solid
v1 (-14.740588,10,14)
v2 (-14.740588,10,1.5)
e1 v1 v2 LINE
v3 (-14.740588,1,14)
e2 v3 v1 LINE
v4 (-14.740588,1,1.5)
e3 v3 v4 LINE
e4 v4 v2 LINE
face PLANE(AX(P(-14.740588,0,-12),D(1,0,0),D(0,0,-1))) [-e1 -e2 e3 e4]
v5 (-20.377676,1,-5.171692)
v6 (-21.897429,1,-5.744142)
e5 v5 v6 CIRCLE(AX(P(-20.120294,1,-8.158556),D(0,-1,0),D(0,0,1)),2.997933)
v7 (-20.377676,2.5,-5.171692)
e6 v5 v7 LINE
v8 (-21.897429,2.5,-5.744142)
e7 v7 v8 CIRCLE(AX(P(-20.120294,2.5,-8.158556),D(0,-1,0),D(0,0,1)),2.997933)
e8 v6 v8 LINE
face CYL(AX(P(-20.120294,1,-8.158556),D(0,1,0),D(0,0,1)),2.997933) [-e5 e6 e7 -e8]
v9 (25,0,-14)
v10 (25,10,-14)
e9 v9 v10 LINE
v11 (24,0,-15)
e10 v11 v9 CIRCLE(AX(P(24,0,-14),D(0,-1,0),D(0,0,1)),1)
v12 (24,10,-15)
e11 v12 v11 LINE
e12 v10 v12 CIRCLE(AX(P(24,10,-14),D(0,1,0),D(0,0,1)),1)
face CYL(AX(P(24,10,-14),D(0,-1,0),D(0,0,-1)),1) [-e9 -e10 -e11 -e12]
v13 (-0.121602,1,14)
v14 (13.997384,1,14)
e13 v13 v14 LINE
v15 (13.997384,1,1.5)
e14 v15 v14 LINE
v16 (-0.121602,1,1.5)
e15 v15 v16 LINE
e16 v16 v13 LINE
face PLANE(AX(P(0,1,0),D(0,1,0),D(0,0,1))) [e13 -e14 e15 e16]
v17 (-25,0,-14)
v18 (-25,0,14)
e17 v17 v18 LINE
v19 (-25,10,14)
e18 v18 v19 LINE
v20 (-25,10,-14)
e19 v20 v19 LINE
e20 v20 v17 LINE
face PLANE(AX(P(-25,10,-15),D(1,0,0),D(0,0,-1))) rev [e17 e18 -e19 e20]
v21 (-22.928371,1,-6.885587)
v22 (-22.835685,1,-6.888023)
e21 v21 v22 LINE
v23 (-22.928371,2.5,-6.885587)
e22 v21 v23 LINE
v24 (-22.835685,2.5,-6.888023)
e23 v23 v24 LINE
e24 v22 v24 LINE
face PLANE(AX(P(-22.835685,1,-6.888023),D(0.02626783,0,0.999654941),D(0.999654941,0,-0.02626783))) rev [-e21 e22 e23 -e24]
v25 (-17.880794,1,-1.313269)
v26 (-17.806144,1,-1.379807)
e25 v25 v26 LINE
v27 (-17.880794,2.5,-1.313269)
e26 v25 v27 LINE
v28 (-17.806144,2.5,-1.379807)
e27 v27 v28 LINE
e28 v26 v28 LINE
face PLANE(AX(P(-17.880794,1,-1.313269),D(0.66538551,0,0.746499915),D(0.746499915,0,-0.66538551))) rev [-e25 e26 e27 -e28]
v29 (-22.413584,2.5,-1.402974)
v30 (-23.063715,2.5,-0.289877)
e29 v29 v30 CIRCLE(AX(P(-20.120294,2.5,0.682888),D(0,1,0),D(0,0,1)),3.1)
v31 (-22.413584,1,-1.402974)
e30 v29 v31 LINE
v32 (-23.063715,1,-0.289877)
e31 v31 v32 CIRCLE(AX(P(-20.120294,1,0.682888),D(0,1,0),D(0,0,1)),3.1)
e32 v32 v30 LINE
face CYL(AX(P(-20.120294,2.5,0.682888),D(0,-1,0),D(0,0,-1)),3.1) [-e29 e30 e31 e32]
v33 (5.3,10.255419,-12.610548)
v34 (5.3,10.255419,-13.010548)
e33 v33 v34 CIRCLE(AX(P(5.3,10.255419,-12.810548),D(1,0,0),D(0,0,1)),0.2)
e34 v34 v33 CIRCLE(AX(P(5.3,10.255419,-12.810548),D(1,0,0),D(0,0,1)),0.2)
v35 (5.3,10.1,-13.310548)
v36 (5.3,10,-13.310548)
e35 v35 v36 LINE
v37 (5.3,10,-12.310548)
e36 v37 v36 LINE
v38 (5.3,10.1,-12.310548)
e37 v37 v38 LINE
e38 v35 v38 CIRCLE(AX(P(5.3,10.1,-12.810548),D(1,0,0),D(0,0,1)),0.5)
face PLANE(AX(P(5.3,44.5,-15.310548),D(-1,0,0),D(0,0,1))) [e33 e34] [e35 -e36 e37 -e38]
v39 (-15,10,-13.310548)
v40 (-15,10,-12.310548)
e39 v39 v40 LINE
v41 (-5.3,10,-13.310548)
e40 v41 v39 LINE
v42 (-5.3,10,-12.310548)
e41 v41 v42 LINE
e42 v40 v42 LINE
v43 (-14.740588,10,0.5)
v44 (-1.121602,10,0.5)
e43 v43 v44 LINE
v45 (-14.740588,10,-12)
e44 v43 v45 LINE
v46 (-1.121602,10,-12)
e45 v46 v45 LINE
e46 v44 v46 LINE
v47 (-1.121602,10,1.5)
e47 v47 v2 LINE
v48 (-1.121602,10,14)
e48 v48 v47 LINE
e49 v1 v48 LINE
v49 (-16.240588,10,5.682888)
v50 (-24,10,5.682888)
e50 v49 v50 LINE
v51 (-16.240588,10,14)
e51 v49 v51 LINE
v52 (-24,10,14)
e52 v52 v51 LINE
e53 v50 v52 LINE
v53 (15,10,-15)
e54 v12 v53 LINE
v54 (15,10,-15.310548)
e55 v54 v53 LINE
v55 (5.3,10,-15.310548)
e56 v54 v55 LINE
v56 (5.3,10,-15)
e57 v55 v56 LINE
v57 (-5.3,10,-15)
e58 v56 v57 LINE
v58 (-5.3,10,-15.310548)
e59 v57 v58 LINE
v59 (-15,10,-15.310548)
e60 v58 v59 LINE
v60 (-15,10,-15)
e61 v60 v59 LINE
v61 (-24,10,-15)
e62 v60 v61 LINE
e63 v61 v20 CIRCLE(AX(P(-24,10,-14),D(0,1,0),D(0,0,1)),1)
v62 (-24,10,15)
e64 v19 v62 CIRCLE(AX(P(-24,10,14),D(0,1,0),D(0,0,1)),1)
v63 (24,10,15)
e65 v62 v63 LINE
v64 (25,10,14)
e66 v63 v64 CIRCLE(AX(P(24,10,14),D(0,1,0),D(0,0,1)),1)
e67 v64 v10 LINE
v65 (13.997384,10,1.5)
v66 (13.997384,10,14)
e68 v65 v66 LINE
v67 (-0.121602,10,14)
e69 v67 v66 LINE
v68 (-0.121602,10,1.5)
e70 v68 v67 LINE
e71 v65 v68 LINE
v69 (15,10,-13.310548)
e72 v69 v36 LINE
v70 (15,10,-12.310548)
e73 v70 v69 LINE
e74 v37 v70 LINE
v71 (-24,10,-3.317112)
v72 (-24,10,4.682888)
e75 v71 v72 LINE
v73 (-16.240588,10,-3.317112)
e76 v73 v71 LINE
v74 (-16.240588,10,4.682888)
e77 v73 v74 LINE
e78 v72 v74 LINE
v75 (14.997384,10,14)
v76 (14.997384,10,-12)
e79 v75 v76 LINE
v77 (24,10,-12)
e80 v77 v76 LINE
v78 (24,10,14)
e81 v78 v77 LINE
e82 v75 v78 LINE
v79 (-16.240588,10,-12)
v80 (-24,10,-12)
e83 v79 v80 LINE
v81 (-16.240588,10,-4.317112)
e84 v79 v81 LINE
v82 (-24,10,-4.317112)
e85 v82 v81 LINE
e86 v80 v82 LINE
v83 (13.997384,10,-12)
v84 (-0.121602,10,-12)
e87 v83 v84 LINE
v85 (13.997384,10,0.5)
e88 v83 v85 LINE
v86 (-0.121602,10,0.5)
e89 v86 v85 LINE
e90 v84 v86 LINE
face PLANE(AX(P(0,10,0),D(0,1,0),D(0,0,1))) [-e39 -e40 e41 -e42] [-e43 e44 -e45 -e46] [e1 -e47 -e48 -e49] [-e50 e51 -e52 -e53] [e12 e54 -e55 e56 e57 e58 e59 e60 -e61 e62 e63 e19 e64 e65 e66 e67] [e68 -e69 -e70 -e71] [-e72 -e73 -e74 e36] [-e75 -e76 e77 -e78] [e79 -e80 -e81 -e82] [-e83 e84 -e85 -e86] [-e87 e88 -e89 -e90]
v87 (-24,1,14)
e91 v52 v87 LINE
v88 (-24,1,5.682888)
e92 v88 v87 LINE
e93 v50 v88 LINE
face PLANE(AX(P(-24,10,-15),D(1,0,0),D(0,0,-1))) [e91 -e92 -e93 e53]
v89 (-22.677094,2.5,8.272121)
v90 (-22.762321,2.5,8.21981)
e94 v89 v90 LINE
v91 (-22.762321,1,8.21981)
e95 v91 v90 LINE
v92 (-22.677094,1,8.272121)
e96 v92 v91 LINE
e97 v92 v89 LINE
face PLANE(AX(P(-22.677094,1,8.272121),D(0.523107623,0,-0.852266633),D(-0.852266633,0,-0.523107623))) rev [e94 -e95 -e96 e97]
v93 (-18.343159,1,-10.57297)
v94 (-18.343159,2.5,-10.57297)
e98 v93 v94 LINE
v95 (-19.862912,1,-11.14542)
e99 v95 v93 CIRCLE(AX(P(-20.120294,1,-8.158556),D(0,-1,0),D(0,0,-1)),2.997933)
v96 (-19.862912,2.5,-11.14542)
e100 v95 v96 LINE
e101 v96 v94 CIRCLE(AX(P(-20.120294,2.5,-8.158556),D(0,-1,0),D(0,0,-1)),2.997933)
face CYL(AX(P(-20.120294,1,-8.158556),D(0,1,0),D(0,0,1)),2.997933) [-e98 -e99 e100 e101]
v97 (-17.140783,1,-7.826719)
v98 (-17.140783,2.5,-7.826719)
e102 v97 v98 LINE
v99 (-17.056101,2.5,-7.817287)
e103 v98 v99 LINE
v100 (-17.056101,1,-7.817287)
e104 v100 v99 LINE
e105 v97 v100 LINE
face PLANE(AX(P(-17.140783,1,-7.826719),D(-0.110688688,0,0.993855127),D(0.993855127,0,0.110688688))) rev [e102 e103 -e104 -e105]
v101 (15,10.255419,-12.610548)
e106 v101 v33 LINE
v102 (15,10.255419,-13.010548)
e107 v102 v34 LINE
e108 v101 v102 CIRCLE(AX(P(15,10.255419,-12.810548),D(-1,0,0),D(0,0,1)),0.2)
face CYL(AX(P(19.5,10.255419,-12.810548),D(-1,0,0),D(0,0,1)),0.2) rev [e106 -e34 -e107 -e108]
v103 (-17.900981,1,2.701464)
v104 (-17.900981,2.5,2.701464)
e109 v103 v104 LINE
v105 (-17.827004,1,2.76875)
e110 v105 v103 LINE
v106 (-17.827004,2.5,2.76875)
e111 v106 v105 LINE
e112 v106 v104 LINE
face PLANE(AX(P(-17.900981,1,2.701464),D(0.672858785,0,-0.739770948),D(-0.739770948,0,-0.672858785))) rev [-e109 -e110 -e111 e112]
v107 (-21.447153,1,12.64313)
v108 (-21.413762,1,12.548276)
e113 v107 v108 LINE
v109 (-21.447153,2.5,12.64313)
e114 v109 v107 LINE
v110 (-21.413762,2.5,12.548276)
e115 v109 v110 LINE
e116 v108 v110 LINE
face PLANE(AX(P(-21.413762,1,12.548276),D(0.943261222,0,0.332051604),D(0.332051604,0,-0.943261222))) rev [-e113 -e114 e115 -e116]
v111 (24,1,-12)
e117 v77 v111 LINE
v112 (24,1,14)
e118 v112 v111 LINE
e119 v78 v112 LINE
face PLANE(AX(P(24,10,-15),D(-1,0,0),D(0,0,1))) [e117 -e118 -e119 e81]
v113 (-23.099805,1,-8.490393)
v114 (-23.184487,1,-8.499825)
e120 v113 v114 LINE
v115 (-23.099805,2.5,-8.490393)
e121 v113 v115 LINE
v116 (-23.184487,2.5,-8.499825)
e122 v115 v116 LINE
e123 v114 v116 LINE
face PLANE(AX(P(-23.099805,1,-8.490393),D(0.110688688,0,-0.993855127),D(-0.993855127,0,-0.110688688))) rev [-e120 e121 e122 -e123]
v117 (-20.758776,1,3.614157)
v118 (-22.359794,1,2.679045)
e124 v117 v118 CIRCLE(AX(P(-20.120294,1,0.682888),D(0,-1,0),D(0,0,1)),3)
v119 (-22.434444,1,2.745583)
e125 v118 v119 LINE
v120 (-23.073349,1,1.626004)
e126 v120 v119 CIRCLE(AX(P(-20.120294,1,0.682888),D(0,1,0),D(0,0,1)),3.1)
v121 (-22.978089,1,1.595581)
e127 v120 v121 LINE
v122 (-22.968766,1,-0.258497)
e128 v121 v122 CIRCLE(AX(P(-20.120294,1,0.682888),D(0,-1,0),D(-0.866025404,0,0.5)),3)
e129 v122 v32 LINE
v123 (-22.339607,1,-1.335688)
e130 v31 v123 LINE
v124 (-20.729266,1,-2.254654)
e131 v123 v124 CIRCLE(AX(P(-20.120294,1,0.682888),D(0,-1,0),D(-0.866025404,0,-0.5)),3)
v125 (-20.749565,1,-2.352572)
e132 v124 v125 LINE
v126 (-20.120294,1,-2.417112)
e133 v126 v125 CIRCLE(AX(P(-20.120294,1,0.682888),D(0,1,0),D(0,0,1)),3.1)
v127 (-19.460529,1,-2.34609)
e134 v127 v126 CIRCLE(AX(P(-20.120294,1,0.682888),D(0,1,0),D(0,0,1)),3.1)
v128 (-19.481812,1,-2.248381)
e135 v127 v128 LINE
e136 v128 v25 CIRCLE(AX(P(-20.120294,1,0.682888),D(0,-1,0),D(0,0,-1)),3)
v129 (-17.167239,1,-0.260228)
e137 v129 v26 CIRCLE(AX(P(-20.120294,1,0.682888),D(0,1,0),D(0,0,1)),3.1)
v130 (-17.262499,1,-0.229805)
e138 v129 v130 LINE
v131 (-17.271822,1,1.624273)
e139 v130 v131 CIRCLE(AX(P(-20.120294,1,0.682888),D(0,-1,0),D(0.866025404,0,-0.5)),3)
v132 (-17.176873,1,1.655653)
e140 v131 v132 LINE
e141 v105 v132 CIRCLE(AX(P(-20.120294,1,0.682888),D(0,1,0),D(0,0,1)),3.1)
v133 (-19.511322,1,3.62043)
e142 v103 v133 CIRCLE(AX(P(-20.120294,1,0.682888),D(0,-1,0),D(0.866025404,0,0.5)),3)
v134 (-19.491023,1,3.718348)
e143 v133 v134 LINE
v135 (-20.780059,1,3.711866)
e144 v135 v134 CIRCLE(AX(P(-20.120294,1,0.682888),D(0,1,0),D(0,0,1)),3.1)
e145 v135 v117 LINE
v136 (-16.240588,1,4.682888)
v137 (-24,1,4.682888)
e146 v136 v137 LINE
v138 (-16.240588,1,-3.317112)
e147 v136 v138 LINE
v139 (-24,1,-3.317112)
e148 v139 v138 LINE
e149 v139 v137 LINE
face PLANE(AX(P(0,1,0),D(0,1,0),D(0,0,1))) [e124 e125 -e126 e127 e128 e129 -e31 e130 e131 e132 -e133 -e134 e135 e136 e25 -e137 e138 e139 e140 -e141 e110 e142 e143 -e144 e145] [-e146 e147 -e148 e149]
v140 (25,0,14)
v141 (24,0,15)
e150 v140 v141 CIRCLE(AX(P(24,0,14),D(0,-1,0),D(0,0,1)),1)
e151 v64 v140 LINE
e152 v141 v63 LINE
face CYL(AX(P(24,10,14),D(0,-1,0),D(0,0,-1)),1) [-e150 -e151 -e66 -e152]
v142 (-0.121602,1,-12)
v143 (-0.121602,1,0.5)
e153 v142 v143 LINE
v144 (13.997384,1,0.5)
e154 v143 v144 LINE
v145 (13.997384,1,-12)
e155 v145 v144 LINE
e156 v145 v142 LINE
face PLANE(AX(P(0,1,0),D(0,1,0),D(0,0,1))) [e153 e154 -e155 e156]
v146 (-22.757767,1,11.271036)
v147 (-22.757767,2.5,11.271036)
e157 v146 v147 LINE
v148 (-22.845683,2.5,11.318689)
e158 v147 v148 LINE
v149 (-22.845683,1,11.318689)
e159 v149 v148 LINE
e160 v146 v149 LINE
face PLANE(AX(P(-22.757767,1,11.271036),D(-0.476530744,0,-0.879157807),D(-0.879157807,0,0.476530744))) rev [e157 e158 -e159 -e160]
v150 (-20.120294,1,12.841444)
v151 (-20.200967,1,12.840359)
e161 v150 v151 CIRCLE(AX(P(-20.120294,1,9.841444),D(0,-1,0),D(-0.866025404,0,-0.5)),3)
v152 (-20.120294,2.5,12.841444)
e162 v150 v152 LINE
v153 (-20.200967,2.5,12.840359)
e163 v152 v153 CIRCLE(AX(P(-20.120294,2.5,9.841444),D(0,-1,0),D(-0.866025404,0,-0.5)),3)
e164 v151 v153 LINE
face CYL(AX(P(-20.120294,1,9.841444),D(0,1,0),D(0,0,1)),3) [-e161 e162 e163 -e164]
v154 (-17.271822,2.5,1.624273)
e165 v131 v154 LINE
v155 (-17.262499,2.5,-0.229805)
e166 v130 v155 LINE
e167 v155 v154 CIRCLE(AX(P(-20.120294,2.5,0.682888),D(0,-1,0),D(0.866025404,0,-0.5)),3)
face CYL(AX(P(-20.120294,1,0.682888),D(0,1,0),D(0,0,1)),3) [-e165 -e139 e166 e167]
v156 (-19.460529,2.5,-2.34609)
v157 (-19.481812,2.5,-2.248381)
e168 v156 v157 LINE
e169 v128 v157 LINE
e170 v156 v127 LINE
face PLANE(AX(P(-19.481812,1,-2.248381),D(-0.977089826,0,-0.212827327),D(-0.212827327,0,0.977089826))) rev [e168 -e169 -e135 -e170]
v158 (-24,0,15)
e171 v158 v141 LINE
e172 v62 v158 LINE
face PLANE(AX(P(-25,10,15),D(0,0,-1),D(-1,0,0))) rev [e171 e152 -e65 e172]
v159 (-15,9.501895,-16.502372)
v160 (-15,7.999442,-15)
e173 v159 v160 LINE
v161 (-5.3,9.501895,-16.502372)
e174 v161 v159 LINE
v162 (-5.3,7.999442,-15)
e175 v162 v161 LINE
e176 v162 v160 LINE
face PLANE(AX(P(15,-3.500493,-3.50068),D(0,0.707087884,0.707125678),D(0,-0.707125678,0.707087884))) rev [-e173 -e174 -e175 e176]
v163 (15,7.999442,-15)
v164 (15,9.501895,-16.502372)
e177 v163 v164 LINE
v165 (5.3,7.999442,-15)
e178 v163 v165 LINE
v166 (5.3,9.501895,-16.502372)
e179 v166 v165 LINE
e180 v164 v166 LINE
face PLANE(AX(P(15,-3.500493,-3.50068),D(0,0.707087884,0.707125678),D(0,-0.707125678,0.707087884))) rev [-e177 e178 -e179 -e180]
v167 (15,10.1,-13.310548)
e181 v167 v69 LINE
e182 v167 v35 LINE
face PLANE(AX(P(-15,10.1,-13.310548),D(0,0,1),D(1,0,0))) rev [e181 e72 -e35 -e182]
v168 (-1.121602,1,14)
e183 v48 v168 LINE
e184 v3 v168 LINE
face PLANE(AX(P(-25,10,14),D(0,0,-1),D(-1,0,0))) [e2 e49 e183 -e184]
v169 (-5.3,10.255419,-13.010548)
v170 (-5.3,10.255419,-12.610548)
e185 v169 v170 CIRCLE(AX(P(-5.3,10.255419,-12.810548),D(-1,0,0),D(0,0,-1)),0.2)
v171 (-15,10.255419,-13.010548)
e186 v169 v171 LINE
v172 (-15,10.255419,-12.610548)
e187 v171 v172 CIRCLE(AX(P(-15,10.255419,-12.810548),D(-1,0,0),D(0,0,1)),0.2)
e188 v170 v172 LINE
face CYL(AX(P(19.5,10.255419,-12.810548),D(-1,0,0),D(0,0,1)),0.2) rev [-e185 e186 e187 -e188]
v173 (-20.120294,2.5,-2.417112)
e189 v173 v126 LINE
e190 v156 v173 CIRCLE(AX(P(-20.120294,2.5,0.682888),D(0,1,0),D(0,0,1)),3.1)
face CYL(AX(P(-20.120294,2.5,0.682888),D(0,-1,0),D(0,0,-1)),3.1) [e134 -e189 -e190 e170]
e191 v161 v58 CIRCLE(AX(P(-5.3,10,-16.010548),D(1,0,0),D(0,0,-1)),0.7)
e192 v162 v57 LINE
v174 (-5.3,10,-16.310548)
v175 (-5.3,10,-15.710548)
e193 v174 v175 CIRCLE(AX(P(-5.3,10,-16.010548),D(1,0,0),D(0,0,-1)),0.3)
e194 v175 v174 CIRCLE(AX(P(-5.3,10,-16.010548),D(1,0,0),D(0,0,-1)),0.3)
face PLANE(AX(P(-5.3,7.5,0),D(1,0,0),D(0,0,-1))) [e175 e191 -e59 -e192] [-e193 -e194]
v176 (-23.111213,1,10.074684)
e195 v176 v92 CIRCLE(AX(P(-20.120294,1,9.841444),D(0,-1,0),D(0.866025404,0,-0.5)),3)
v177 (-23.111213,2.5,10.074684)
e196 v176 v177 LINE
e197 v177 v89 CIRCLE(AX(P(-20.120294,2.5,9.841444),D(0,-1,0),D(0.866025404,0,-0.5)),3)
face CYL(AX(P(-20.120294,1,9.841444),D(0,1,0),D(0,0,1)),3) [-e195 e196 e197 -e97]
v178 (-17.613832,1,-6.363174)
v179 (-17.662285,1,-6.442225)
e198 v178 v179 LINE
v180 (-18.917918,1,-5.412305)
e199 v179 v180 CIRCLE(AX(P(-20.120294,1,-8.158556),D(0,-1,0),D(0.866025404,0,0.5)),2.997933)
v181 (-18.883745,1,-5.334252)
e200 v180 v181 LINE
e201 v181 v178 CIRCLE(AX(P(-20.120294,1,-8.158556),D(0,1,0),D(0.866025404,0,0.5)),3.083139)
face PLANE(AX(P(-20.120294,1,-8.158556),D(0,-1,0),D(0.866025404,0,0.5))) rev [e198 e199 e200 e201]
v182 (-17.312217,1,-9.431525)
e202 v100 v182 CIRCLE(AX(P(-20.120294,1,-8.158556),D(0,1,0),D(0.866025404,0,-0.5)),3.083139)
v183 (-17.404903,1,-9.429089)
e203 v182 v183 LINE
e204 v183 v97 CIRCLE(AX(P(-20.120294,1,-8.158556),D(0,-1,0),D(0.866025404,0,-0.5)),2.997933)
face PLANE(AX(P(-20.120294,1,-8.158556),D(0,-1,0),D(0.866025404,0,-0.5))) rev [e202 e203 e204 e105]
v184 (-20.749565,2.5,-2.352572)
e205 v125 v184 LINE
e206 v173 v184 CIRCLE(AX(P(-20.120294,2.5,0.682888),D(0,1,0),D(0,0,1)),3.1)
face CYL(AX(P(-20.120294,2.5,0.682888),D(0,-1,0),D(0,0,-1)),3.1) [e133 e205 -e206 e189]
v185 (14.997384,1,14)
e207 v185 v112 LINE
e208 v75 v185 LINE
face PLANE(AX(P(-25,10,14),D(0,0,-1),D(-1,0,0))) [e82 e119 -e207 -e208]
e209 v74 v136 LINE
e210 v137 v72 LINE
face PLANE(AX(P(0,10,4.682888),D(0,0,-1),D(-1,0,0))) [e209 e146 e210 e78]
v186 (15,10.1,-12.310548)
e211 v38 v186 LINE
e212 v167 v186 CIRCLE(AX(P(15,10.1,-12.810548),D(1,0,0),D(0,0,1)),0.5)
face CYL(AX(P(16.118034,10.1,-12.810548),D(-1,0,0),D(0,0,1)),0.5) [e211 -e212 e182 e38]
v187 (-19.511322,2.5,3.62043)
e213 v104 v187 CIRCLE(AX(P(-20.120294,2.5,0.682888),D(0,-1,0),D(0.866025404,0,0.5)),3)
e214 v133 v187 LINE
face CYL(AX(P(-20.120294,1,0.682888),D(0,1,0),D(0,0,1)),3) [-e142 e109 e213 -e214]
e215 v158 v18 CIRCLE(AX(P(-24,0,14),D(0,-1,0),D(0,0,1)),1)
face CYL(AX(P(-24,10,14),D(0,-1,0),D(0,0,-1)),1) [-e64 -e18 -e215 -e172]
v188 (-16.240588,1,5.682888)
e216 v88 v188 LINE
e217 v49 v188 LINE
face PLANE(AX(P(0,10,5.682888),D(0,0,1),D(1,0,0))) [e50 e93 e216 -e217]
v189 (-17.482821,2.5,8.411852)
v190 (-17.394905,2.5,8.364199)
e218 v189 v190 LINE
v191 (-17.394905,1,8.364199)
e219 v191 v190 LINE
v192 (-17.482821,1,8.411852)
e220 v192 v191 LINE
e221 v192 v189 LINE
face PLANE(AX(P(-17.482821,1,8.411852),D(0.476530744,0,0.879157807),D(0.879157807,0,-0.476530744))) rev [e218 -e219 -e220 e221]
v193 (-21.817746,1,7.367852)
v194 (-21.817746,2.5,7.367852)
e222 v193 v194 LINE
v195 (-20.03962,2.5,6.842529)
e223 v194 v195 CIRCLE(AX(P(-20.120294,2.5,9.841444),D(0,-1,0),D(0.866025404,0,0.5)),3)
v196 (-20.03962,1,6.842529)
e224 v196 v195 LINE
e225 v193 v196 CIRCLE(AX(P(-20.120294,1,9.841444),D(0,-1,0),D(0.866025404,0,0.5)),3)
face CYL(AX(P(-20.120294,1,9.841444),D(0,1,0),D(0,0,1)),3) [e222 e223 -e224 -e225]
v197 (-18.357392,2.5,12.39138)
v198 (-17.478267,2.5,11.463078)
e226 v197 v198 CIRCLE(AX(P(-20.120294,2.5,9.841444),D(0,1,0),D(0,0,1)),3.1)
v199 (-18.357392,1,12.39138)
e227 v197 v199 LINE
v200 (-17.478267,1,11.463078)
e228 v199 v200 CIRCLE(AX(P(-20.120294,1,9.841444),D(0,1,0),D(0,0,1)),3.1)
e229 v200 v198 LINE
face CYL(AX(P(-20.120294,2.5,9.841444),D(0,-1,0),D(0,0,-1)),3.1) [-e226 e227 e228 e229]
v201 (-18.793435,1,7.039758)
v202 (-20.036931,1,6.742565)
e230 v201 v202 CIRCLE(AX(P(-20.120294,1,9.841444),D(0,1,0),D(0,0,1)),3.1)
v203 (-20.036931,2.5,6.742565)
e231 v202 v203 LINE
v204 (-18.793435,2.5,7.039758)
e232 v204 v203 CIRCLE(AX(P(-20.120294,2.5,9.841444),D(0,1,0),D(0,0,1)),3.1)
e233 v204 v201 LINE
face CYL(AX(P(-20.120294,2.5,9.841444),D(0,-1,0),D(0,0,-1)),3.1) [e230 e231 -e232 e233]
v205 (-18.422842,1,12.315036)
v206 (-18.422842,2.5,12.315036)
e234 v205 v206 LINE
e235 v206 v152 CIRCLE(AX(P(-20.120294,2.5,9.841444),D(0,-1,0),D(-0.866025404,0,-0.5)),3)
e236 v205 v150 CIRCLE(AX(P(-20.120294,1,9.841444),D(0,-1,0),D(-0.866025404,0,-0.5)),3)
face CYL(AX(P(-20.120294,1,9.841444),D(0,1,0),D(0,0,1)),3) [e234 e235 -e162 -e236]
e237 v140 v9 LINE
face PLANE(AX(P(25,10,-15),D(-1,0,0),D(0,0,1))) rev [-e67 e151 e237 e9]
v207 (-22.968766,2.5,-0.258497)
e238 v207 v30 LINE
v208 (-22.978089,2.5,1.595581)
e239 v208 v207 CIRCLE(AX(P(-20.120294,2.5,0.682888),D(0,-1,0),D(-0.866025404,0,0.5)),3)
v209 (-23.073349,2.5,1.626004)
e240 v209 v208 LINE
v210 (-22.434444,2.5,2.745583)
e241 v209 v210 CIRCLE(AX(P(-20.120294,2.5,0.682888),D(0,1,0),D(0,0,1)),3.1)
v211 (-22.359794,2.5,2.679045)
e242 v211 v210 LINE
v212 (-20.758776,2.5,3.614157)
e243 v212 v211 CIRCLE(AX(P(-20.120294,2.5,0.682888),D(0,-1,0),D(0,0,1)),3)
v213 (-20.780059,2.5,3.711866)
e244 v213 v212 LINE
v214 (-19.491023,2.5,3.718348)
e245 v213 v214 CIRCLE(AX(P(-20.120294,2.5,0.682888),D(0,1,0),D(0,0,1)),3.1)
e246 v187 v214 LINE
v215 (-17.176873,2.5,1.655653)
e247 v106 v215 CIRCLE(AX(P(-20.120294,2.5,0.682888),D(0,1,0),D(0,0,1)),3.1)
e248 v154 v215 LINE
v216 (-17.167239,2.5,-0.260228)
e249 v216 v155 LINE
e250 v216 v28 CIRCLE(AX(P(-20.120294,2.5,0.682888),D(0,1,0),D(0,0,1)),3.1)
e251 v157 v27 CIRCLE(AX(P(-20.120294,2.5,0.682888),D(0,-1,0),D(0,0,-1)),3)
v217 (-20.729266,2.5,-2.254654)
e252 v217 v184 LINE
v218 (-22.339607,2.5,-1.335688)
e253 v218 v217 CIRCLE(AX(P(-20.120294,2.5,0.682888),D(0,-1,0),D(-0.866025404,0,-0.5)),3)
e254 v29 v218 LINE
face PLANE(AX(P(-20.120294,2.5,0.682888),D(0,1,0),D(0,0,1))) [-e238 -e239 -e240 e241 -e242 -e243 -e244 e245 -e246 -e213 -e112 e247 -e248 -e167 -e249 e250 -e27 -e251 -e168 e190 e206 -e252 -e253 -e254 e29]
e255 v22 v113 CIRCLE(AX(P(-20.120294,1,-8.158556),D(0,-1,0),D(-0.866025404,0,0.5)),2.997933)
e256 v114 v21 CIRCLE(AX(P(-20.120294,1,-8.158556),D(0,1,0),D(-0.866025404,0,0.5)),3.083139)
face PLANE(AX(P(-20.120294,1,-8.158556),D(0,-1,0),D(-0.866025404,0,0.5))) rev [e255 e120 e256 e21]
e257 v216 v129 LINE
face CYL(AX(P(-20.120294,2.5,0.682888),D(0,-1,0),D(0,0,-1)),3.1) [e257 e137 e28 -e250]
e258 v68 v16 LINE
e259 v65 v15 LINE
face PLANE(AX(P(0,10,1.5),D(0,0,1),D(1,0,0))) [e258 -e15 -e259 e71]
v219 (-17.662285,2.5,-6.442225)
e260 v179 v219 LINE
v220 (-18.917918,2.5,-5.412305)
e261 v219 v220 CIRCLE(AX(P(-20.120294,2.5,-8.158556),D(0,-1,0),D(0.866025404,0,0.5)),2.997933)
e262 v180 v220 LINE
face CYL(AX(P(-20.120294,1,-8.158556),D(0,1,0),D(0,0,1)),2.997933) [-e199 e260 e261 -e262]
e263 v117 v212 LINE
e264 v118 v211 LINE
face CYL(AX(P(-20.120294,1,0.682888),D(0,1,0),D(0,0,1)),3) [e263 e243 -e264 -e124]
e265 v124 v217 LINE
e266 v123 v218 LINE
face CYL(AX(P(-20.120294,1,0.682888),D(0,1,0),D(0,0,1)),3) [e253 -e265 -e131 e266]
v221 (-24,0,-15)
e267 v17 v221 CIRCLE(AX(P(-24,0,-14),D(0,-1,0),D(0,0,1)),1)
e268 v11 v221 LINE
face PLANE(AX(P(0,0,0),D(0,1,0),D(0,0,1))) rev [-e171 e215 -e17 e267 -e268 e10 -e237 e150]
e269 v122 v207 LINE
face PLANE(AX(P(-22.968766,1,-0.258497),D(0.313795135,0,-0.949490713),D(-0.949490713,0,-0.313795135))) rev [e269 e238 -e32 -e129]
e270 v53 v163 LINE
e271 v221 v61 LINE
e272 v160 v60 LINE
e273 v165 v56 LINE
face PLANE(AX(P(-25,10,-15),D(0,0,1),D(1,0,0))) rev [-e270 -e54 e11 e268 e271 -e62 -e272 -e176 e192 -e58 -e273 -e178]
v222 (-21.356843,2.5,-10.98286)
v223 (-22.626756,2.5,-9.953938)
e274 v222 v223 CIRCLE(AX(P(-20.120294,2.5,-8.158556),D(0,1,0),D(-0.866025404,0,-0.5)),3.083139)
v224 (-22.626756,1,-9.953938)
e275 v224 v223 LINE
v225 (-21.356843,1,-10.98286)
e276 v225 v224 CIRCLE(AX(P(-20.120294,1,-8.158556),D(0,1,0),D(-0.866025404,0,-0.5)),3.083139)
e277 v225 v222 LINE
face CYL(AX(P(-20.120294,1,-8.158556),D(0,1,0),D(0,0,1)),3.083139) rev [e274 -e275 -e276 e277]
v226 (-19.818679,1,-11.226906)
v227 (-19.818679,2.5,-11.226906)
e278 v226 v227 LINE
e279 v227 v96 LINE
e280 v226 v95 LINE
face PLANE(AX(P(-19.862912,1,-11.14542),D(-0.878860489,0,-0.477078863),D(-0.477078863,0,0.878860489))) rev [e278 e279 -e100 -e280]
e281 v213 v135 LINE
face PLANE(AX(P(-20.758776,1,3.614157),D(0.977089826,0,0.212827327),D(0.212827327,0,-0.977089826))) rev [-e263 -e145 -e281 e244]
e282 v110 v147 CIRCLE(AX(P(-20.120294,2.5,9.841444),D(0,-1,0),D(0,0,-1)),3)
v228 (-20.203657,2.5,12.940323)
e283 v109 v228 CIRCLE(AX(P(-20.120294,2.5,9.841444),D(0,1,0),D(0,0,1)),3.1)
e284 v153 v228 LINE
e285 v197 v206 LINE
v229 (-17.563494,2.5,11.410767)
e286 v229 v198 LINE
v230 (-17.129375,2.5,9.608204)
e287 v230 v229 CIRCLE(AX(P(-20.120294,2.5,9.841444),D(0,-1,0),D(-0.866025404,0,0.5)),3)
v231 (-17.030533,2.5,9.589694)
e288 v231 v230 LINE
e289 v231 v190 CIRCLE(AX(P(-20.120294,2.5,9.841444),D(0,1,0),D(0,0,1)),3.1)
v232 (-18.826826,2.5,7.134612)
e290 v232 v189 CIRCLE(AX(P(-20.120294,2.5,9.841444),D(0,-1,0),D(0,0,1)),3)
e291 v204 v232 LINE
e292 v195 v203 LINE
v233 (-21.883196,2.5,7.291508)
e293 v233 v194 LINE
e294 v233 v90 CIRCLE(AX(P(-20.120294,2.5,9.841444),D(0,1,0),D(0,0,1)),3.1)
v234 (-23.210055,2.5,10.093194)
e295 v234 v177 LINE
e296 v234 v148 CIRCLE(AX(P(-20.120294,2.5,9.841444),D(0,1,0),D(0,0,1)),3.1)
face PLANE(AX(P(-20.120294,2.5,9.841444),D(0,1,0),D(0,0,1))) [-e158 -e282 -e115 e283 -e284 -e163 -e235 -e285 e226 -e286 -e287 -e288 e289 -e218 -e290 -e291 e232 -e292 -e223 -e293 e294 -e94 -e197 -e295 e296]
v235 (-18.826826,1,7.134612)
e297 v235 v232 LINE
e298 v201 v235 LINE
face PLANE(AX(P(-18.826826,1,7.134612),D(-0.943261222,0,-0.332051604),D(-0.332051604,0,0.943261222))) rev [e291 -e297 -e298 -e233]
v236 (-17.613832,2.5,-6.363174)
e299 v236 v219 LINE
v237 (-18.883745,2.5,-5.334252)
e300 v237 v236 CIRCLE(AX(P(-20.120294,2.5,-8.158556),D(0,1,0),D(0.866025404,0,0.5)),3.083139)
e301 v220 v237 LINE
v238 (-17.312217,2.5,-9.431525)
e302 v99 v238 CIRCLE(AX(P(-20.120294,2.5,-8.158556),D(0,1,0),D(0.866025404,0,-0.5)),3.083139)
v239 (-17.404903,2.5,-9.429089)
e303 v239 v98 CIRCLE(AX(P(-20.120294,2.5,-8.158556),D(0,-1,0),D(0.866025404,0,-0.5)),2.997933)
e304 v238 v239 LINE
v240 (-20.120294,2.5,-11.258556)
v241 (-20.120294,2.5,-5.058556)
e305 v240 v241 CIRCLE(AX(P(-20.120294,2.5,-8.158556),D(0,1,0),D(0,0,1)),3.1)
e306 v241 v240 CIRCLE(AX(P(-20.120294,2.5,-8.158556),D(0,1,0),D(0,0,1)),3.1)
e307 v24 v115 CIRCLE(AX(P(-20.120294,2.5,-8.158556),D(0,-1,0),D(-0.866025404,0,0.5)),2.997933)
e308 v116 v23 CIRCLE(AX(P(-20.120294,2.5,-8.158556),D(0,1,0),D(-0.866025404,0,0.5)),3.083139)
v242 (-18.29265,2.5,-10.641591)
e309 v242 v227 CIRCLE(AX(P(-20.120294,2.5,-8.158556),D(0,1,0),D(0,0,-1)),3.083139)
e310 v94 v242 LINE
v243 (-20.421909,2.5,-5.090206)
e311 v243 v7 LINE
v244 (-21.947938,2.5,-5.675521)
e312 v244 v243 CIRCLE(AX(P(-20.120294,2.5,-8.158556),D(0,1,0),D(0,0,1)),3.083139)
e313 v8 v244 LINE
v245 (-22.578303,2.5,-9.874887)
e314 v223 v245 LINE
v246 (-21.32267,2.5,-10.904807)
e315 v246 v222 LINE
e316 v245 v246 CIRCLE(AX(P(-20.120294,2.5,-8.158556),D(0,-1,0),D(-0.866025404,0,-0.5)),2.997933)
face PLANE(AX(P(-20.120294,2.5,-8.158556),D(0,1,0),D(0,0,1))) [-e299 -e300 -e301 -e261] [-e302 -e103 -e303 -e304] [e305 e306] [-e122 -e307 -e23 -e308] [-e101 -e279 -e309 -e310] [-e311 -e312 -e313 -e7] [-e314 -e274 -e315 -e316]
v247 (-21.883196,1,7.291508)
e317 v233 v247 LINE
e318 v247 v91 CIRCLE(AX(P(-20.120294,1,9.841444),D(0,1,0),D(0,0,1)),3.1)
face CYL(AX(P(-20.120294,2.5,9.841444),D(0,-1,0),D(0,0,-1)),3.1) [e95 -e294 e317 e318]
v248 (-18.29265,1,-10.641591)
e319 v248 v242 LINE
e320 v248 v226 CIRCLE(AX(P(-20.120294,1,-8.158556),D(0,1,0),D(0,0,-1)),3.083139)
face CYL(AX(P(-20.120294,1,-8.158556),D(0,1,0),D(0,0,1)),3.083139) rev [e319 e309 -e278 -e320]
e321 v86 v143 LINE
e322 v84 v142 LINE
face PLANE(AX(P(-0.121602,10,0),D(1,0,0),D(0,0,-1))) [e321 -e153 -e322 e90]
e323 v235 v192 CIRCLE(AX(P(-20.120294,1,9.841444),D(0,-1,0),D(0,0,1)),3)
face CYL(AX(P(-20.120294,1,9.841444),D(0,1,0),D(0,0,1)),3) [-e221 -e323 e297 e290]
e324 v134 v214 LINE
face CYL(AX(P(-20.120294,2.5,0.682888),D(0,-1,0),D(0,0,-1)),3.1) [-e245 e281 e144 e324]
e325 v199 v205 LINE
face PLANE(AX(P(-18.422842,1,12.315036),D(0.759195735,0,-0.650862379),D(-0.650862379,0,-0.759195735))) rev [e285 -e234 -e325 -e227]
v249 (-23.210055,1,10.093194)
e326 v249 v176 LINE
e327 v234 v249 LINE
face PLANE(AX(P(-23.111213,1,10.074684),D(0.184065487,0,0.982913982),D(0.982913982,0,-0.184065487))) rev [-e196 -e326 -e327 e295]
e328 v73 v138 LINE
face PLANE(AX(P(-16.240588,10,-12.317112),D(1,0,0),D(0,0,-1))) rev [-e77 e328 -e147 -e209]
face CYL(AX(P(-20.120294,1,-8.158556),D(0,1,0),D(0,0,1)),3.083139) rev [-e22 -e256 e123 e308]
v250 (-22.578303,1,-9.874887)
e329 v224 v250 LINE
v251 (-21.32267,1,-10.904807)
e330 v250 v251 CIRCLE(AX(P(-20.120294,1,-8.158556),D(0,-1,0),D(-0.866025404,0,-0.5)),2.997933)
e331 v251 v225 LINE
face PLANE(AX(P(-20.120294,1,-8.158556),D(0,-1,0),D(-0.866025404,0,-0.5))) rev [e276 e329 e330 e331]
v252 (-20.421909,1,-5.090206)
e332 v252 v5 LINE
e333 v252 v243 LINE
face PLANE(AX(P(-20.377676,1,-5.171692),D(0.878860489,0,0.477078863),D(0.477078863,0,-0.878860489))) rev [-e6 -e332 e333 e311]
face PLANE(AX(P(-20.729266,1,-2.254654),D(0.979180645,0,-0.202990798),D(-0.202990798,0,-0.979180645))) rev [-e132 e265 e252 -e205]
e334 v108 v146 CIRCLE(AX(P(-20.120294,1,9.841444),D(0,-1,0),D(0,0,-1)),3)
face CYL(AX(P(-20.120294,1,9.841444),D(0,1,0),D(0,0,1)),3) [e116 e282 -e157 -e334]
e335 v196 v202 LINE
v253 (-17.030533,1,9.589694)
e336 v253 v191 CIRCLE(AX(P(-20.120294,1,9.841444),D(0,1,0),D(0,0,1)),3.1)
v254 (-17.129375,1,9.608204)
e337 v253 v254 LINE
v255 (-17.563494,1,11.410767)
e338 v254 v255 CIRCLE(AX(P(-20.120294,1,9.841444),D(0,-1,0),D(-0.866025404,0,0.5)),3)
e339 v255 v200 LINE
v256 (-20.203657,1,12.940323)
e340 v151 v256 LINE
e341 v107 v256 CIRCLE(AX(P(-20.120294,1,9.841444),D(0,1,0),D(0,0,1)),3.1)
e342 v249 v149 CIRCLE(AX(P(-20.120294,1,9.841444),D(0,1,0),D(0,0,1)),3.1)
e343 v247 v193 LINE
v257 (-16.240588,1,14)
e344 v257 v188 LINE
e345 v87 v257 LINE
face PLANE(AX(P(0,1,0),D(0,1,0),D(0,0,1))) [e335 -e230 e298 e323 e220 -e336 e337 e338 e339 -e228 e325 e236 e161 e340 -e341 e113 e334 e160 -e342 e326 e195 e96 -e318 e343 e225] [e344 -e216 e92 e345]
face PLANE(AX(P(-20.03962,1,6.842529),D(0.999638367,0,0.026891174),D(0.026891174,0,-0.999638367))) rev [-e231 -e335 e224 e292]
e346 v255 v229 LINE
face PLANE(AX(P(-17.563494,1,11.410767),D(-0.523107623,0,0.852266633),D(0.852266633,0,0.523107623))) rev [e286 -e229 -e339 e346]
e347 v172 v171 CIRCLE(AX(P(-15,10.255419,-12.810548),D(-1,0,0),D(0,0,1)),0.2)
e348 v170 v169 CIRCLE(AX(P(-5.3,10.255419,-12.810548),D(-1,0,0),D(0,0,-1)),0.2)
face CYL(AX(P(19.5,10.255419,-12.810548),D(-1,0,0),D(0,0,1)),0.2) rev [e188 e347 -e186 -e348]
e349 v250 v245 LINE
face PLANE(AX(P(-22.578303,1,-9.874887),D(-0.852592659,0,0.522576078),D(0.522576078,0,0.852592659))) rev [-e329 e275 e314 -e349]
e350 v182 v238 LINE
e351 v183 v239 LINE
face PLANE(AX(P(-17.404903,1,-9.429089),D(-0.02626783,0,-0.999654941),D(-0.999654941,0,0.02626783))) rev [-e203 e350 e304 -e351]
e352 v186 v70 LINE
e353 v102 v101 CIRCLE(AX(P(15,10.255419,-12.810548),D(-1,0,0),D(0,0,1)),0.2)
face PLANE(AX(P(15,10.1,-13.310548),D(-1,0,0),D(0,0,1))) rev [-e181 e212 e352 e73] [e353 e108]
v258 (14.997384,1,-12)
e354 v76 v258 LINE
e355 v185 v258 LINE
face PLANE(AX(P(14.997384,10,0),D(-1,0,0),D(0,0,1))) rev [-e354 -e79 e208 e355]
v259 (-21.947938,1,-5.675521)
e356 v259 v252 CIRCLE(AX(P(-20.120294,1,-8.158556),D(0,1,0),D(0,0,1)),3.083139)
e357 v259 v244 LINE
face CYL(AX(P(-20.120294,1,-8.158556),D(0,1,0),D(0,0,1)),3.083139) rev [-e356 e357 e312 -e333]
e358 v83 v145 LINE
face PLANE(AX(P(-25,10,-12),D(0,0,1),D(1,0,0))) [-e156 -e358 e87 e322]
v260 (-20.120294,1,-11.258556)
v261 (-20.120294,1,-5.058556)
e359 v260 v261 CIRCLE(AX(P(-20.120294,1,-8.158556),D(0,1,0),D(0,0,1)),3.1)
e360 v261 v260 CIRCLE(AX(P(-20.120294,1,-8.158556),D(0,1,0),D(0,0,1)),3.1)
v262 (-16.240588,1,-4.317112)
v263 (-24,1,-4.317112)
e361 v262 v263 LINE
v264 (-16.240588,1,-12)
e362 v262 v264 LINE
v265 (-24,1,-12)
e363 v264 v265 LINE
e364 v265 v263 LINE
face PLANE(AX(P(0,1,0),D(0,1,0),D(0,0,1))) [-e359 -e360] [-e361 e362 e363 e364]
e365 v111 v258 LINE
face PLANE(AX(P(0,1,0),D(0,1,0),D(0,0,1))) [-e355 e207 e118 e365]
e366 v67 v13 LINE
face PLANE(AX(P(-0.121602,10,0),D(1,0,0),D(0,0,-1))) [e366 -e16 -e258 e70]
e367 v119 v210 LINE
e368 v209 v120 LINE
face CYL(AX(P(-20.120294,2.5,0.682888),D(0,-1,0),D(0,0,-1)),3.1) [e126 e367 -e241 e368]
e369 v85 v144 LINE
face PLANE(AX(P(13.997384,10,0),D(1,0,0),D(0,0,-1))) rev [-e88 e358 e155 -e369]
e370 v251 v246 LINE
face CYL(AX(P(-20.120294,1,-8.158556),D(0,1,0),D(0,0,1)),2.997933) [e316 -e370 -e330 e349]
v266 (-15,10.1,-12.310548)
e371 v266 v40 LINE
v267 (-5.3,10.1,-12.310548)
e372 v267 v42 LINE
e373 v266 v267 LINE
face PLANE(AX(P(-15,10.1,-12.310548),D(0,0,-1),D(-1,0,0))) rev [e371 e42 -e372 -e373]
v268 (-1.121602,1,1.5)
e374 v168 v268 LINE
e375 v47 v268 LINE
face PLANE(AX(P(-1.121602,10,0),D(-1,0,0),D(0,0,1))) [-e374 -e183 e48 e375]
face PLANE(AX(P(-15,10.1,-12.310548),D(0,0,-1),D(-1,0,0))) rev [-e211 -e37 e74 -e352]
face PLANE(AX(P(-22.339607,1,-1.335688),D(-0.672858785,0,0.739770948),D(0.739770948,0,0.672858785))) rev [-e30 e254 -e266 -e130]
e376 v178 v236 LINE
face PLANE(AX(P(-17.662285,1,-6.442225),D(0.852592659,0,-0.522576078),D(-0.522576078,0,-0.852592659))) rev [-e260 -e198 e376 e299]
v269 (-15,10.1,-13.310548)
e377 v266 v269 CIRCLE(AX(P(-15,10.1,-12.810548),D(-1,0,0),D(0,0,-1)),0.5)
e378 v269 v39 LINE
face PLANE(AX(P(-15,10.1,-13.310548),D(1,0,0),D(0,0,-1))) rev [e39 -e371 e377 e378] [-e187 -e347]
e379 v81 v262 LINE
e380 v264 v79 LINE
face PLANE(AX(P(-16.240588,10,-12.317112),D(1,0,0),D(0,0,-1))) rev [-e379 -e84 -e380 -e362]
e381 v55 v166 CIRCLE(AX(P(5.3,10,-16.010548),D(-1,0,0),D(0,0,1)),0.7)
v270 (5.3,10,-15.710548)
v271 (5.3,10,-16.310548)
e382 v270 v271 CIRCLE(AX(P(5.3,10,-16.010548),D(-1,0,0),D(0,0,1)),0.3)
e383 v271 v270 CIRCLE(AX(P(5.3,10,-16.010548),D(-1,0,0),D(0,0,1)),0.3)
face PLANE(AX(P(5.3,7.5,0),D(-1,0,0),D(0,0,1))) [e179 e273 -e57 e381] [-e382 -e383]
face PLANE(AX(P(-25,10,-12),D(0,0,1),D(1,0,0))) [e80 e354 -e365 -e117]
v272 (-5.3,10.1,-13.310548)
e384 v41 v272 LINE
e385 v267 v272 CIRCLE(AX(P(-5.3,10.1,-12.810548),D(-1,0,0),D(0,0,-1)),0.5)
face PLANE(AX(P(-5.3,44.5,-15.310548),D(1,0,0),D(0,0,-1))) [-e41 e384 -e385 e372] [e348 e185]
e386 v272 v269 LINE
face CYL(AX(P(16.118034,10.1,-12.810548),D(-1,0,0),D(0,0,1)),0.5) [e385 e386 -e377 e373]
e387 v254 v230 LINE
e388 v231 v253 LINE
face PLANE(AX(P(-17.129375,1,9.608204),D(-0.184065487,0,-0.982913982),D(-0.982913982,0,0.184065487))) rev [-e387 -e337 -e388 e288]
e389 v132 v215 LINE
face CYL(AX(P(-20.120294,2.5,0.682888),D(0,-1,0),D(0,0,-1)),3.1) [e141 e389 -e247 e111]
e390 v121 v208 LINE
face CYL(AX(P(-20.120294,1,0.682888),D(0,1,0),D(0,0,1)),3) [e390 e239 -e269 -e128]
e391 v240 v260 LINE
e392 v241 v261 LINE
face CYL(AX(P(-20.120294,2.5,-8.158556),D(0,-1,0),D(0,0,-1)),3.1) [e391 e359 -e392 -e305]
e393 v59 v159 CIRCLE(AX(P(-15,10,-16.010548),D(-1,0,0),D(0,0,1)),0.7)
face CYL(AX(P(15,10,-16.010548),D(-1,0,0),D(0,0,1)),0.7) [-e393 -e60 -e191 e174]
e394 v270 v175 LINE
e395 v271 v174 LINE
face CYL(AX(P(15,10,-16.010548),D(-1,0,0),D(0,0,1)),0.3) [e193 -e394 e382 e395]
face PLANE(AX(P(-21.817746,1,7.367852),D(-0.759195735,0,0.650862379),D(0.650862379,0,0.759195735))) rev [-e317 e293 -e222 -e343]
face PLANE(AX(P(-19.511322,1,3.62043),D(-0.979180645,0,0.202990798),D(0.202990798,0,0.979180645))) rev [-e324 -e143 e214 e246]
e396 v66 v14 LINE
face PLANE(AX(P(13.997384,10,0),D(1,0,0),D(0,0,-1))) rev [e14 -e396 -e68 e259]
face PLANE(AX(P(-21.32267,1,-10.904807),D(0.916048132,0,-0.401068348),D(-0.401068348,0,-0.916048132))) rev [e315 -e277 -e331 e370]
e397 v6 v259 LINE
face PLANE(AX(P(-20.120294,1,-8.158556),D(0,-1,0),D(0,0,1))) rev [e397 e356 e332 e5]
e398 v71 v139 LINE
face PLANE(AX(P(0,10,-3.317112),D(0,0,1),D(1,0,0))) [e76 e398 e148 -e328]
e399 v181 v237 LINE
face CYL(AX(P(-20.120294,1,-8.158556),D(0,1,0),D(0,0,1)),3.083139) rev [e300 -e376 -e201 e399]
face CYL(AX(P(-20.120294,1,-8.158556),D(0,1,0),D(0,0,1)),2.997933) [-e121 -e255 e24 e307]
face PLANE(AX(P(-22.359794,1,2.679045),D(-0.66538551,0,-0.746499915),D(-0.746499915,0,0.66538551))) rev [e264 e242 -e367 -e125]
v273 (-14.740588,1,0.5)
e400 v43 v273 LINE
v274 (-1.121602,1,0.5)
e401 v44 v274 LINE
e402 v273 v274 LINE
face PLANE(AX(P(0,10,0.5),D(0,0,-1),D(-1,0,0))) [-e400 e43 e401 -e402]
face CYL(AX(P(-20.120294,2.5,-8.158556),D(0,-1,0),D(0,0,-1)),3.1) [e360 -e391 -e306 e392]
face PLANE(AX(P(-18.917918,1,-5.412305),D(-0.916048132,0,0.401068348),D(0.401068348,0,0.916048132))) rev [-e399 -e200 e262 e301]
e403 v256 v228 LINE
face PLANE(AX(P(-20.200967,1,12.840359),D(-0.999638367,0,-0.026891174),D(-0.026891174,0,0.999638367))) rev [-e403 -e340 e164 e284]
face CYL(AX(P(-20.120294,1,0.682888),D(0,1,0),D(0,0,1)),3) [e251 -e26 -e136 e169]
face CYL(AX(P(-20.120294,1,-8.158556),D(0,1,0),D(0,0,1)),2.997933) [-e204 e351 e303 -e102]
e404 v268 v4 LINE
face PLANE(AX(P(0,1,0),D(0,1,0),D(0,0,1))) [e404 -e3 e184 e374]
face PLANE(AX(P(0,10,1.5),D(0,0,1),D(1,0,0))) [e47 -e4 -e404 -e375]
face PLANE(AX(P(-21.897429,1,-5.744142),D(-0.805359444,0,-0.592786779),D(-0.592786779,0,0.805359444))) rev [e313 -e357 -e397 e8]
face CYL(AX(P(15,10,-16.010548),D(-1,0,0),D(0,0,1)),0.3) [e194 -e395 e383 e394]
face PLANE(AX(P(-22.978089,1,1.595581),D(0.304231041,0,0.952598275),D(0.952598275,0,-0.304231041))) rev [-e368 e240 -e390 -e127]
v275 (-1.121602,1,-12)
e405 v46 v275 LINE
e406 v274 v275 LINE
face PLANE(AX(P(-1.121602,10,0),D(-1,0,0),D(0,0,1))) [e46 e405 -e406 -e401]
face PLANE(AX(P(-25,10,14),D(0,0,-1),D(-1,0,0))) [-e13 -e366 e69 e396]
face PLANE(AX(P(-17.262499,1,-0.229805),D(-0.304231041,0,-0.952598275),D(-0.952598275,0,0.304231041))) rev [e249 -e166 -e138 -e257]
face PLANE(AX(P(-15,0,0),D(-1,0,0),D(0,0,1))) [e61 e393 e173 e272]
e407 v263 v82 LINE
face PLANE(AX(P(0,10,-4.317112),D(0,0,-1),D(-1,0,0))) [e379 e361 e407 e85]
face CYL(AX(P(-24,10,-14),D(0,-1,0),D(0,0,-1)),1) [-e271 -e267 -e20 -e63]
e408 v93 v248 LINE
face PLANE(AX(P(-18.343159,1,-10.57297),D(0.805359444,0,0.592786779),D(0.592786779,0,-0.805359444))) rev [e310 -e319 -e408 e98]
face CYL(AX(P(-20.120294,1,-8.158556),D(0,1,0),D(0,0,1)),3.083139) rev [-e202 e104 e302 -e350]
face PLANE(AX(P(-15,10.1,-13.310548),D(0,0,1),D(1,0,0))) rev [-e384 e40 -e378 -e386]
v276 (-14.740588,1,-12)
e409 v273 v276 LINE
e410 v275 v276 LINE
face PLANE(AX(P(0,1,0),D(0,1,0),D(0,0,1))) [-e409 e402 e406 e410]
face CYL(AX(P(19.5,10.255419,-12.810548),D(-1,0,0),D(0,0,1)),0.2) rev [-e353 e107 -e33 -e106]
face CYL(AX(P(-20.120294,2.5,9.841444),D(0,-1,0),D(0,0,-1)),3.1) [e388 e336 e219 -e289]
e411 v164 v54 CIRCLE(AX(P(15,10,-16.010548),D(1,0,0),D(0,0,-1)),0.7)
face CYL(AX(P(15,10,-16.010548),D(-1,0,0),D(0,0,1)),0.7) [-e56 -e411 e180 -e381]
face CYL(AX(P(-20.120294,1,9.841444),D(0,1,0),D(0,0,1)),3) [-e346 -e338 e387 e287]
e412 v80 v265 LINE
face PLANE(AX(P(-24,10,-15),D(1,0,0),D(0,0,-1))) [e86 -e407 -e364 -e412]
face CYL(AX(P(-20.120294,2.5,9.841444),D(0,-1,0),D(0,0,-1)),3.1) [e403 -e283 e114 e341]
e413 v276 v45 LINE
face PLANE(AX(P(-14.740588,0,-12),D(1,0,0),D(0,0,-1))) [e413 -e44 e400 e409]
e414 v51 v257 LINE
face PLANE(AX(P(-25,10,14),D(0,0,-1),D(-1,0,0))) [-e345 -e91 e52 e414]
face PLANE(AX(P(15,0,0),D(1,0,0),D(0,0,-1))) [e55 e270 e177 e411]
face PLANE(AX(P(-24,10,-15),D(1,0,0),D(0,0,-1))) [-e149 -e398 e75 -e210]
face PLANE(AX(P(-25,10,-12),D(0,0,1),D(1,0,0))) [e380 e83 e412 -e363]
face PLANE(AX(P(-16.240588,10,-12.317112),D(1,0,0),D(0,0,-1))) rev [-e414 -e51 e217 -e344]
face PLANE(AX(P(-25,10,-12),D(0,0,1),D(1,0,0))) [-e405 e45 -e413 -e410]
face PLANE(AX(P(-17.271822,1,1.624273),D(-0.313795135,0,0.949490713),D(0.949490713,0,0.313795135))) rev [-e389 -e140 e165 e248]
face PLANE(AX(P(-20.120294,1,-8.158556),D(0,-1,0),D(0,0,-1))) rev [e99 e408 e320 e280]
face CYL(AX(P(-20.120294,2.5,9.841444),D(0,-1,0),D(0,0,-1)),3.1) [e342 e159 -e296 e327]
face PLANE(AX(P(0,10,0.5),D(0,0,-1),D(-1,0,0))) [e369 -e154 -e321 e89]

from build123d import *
from build123d.topology import SkipClean

# Parameters (mm, degrees)
SKETCH1_W                 = 50
SKETCH1_H                 = 30
BOSS_EXTRUDE2_DEPTH       = 10
SHELL3_T                  = -1
SHELL3_THICKNESS_2_FACE_W = 48
SHELL3_THICKNESS_2_FACE_H = 9
SHELL3_THICKNESS_2_DEPTH  = 2
BOSS_EXTRUDE3_DEPTH       = 10
SKETCH3_R                 = 3.1
BOSS_EXTRUDE12_DEPTH      = 1.5
CUT_EXTRUDE2_DEPTH        = 1.5
CIRPATTERN4_COUNT         = 6
SKETCH22_R                = 3.1
BOSS_EXTRUDE13_DEPTH      = 1.5
CUT_EXTRUDE3_DEPTH        = 1.5
CIRPATTERN5_COUNT         = 6
SKETCH27_R                = 3.1
BOSS_EXTRUDE14_DEPTH      = 1.5
CUT_EXTRUDE4_DEPTH        = 1.5
CIRPATTERN6_COUNT         = 6
SKETCH30_W                = 1
SKETCH30_H                = 12.5
SKETCH30_H_2              = 26
BOSS_EXTRUDE15_DEPTH      = 9
SKETCH31_W                = 0.5
SKETCH31_H                = 26
BOSS_EXTRUDE16_DEPTH      = 10
SKETCH32_R                = 0.3
BOSS_EXTRUDE19_DEPTH      = 15
BOSS_EXTRUDE20_START      = 15
SKETCH35_R                = 0.3
BOSS_EXTRUDE20_DEPTH      = 15
SKETCH37_W                = 10.6
SKETCH37_H                = 3.741104567
CUT_EXTRUDE5_DEPTH        = 2.5
SKETCH40_R                = 0.3
BOSS_EXTRUDE21_DEPTH      = 15
FILLET1_R                 = 1
SKETCH66_W                = 30
SKETCH66_H                = 1
BOSS_EXTRUDE22_DEPTH      = 0.1
BOSS_EXTRUDE23_DEPTH      = 30
SKETCH68_R                = 0.2
CUT_EXTRUDE8_DEPTH        = 34.5
SKETCH69_W                = 10.6
SKETCH69_H                = 3.310548063
CUT_EXTRUDE9_DEPTH        = 34.5


with BuildPart() as part:
    # Sketch1 → Boss-Extrude2 (new body)
    with BuildSketch(Plane(origin=(0, 0, 0), x_dir=(1, 0, 0), z_dir=(0, 1, 0))):
        Rectangle(SKETCH1_W, SKETCH1_H)
    extrude(amount=BOSS_EXTRUDE2_DEPTH)

    # Shell3
    shell3_openings = [part.faces().sort_by_distance(p)[0] for p in [
        (0, 10, 0),
    ]]
    offset(amount=SHELL3_T, openings=shell3_openings, kind=Kind.INTERSECTION)

    # Shell3 thickness 2 face (on inner face of the shell) → Shell3 thickness 2 (add)
    with BuildSketch(Plane(origin=(0, 5.5, -14), x_dir=(-1, 0, 0), z_dir=(0, 0, -1))):
        Rectangle(SHELL3_THICKNESS_2_FACE_W, SHELL3_THICKNESS_2_FACE_H)
    extrude(amount=-SHELL3_THICKNESS_2_DEPTH)

    # Sketch2 → Boss-Extrude3 (add)
    with BuildSketch(Plane(origin=(0, 0, 0), x_dir=(1, 0, 0), z_dir=(0, 1, 0))):
        Polygon((-15.24058795, 12.317112), (-16.24058795, 12.317112), (-16.24058795, 4.317112), (-24.24058795, 4.317112), (-24.24058795, 3.317112), (-16.24058795, 3.317112), (-16.24058795, -4.682888), (-24.24058795, -4.682888), (-24.24058795, -5.682888), (-16.24058795, -5.682888), (-16.24058795, -14.110921237), (-15.24058795, -14.110921237), align=None)
    extrude(amount=BOSS_EXTRUDE3_DEPTH)

    # Sketch3 → Boss-Extrude12 (add)
    with BuildSketch(Plane(origin=(0, 1, 0), x_dir=(1, 0, 0), z_dir=(0, 1, 0))):
        with Locations(Location((-20.120293975, 8.158556, 0), (0, 0, 270))):
            Circle(SKETCH3_R)
    extrude(amount=BOSS_EXTRUDE12_DEPTH)

    # Sketch18 → Cut-Extrude2 (cut)
    with BuildSketch(Plane(origin=(0, 2.5, 0), x_dir=(1, 0, 0), z_dir=(0, 1, 0))):
        with BuildLine():
            Line((-18.343158931, 10.572969651), (-18.292649957, 10.641591085))
            ThreePointArc((-18.292649957, 10.641591085), (-19.016172181, 11.037212102), (-19.818678555, 11.226906375))
            Line((-19.818678555, 11.226906375), (-19.862912417, 11.145420071))
            ThreePointArc((-19.862912417, 11.145420071), (-19.063535099, 10.964061823), (-18.343158931, 10.572969651))
        make_face()
    cut_extrude2 = extrude(amount=-CUT_EXTRUDE2_DEPTH, mode=Mode.SUBTRACT)

    # CirPattern4: Cut-Extrude2 ×6 about axis
    cirpattern4_axis = Axis((-20.120293975, 0, -8.158556), (0, 1, 0))
    for i in range(1, CIRPATTERN4_COUNT):
        add(cut_extrude2.rotate(cirpattern4_axis, i * 360 / CIRPATTERN4_COUNT), mode=Mode.SUBTRACT)

    # Sketch22 → Boss-Extrude13 (add)
    with BuildSketch(Plane(origin=(0, 1, 0), x_dir=(1, 0, 0), z_dir=(0, 1, 0))):
        with Locations(Location((-20.120293975, -0.682888, 0), (0, 0, 270))):
            Circle(SKETCH22_R)
    extrude(amount=BOSS_EXTRUDE13_DEPTH)

    # Sketch23 → Cut-Extrude3 (cut)
    with BuildSketch(Plane(origin=(0, 2.5, 0), x_dir=(1, 0, 0), z_dir=(0, 1, 0))):
        with BuildLine():
            Line((-19.481811993, 2.248381479), (-19.436483295, 2.456485436))
            ThreePointArc((-19.436483295, 2.456485436), (-18.499115293, 2.093421016), (-17.725070876, 1.452071043))
            Line((-17.725070876, 1.452071043), (-17.88079423, 1.313268531))
            ThreePointArc((-17.88079423, 1.313268531), (-18.607249441, 1.907613156), (-19.481811993, 2.248381479))
        make_face()
    cut_extrude3 = extrude(amount=-CUT_EXTRUDE3_DEPTH, mode=Mode.SUBTRACT)

    # CirPattern5: Cut-Extrude3 ×6 about axis
    cirpattern5_axis = Axis((-20.120293975, 0, 0.682888), (0, 1, 0))
    for i in range(1, CIRPATTERN5_COUNT):
        add(cut_extrude3.rotate(cirpattern5_axis, i * 360 / CIRPATTERN5_COUNT), mode=Mode.SUBTRACT)

    # Sketch27 → Boss-Extrude14 (add)
    with BuildSketch(Plane(origin=(0, 1, 0), x_dir=(1, 0, 0), z_dir=(0, 1, 0))):
        with Locations(Location((-20.120293975, -9.841444, 0), (0, 0, 270))):
            Circle(SKETCH27_R)
    extrude(amount=BOSS_EXTRUDE14_DEPTH)

    # Sketch28 → Cut-Extrude4 (cut)
    with BuildSketch(Plane(origin=(0, 2.5, 0), x_dir=(1, 0, 0), z_dir=(0, 1, 0))):
        with BuildLine():
            Line((-22.757767397, -11.271036231), (-23.112348525, -11.463230178))
            ThreePointArc((-23.112348525, -11.463230178), (-22.435626904, -12.288964796), (-21.509349026, -12.819812333))
            Line((-21.509349026, -12.819812333), (-21.413761565, -12.548276391))
            ThreePointArc((-21.413761565, -12.548276391), (-22.186911965, -12.016091117), (-22.757767397, -11.271036231))
        make_face()
    cut_extrude4 = extrude(amount=-CUT_EXTRUDE4_DEPTH, mode=Mode.SUBTRACT)

    # CirPattern6: Cut-Extrude4 ×6 about axis
    cirpattern6_axis = Axis((-20.120293975, 0, 9.841444), (0, 1, 0))
    for i in range(1, CIRPATTERN6_COUNT):
        add(cut_extrude4.rotate(cirpattern6_axis, i * 360 / CIRPATTERN6_COUNT), mode=Mode.SUBTRACT)

    # Sketch30 → Boss-Extrude15 (add)
    with BuildSketch(Plane(origin=(0, 1, 0), x_dir=(1, 0, 0), z_dir=(0, 1, 0))):
        Polygon((-1.121602155, -1.5), (-1.121602155, -0.5), (-15.24058795, -0.5), (-15.24058795, -1), (-15.24058795, -1.5), align=None)
        Polygon((13.997383641, -1), (13.997383641, -0.5), (-0.121602155, -0.5), (-0.121602155, -1.5), (13.997383641, -1.5), align=None)
        Polygon((-0.621602155, -0.5), (-0.121602155, -0.5), (-0.121602155, 12), (-1.121602155, 12), (-1.121602155, -0.5), align=None)
        with Locations((-0.621602155, -7.75)):
            Rectangle(SKETCH30_W, SKETCH30_H)
        with Locations((14.497383641, -1)):
            Rectangle(SKETCH30_W, SKETCH30_H_2)
        Polygon((-0.121602155, -1.5), (-0.121602155, -0.5), (-0.621602155, -0.5), (-1.121602155, -0.5), (-1.121602155, -1.5), align=None)
    extrude(amount=BOSS_EXTRUDE15_DEPTH)

    # Sketch31 → Boss-Extrude16 (add)
    with BuildSketch(Plane(origin=(0, 10, 0), x_dir=(1, 0, 0), z_dir=(0, 1, 0))):
        with Locations((-14.99058795, -1)):
            Rectangle(SKETCH31_W, SKETCH31_H)
    extrude(amount=-BOSS_EXTRUDE16_DEPTH)

    # Sketch32 → Boss-Extrude19 (add)
    with BuildSketch(Plane(origin=(0, 0, 0), x_dir=(0, 0, -1), z_dir=(1, 0, 0))):
        with BuildLine():
            Line((15.310548063, 10), (15, 10))
            Line((15, 10), (15, 7.99944207))
            Line((15, 7.99944207), (16.502372161, 9.501894533))
            ThreePointArc((16.502372161, 9.501894533), (16.280476879, 10.645862551), (15.310548063, 10))
        make_face()
        with Locations((16.010548063, 10)):
            Circle(SKETCH32_R, mode=Mode.SUBTRACT)
    extrude(amount=BOSS_EXTRUDE19_DEPTH)

    # Sketch35 → Boss-Extrude20 (add)
    # profile 1 of 2: a face of its own
    with SkipClean():  # the faces are left unmerged after this step: merging them gives an invalid solid
        with BuildSketch(Plane.ZY.offset(BOSS_EXTRUDE20_START)):
            with BuildLine():
                ThreePointArc((-15.310548063, 10), (-15.740619247, 9.354137449), (-16.502372161, 9.501894533))
                Line((-16.502372161, 9.501894533), (-15, 7.99944207))
                Line((-15, 7.99944207), (-15, 10))
                Line((-15, 10), (-15.310548063, 10))
            make_face()
        # profile 2 of 2: a face of its own
        with BuildSketch(Plane.ZY.offset(BOSS_EXTRUDE20_START)):
            with BuildLine():
                ThreePointArc((-15.310548063, 10), (-16.280476879, 10.645862551), (-16.502372161, 9.501894533))
                ThreePointArc((-16.502372161, 9.501894533), (-15.740619247, 9.354137449), (-15.310548063, 10))
            make_face()
            with Locations((-16.010548063, 10)):
                Circle(SKETCH35_R, mode=Mode.SUBTRACT)
        extrude(amount=-BOSS_EXTRUDE20_DEPTH)

    # Sketch37 → Cut-Extrude5 (cut, symmetric)
    with BuildSketch(Plane(origin=(0, 10, 0), x_dir=(1, 0, 0), z_dir=(0, 1, 0))):
        with Locations((0, 16.870552284)):
            Rectangle(SKETCH37_W, SKETCH37_H)
    extrude(amount=CUT_EXTRUDE5_DEPTH, both=True, mode=Mode.SUBTRACT)

    # Sketch40 → Boss-Extrude21 (add, symmetric)
    with BuildSketch(Plane(origin=(0, 0, 0), x_dir=(0, 0, -1), z_dir=(1, 0, 0))):
        with Locations(Location((16.010548063, 10, 0), (0, 0, 180))):
            Circle(SKETCH40_R)
    extrude(amount=BOSS_EXTRUDE21_DEPTH, both=True)

    # Fillet1
    fillet1_edges = [part.edges().sort_by_distance(p)[0] for p in [
        (25, 5, 15),
        (-25, 5, 15),
        (-25, 5, -15),
        (25, 5, -15),
    ]]
    fillet(fillet1_edges, radius=FILLET1_R)

    # Sketch66 → Boss-Extrude22 (add)
    with BuildSketch(Plane(origin=(0, 10, 0), x_dir=(1, 0, 0), z_dir=(0, 1, 0))):
        with Locations((0, 12.810548063)):
            Rectangle(SKETCH66_W, SKETCH66_H)
    extrude(amount=BOSS_EXTRUDE22_DEPTH)

    # Sketch67 → Boss-Extrude23 (add)
    with BuildSketch(Plane.ZY.offset(15)):
        with BuildLine():
            Line((-13.310548063, 10.1), (-12.310548063, 10.1))
            ThreePointArc((-12.310548063, 10.1), (-12.810548063, 10.6), (-13.310548063, 10.1))
        make_face()
    extrude(amount=-BOSS_EXTRUDE23_DEPTH)

    # Sketch68 → Cut-Extrude8 (cut)
    with BuildSketch(Plane.ZY.offset(15)):
        with Locations((-12.810548063, 10.255419354)):
            Circle(SKETCH68_R)
    extrude(amount=-CUT_EXTRUDE8_DEPTH, mode=Mode.SUBTRACT)

    # Sketch69 → Cut-Extrude9 (cut)
    with BuildSketch(Plane(origin=(0, 10, 0), x_dir=(1, 0, 0), z_dir=(0, 1, 0))):
        with Locations((0, 13.655274031)):
            Rectangle(SKETCH69_W, SKETCH69_H)
    extrude(amount=CUT_EXTRUDE9_DEPTH, mode=Mode.SUBTRACT)


solid = part.part
